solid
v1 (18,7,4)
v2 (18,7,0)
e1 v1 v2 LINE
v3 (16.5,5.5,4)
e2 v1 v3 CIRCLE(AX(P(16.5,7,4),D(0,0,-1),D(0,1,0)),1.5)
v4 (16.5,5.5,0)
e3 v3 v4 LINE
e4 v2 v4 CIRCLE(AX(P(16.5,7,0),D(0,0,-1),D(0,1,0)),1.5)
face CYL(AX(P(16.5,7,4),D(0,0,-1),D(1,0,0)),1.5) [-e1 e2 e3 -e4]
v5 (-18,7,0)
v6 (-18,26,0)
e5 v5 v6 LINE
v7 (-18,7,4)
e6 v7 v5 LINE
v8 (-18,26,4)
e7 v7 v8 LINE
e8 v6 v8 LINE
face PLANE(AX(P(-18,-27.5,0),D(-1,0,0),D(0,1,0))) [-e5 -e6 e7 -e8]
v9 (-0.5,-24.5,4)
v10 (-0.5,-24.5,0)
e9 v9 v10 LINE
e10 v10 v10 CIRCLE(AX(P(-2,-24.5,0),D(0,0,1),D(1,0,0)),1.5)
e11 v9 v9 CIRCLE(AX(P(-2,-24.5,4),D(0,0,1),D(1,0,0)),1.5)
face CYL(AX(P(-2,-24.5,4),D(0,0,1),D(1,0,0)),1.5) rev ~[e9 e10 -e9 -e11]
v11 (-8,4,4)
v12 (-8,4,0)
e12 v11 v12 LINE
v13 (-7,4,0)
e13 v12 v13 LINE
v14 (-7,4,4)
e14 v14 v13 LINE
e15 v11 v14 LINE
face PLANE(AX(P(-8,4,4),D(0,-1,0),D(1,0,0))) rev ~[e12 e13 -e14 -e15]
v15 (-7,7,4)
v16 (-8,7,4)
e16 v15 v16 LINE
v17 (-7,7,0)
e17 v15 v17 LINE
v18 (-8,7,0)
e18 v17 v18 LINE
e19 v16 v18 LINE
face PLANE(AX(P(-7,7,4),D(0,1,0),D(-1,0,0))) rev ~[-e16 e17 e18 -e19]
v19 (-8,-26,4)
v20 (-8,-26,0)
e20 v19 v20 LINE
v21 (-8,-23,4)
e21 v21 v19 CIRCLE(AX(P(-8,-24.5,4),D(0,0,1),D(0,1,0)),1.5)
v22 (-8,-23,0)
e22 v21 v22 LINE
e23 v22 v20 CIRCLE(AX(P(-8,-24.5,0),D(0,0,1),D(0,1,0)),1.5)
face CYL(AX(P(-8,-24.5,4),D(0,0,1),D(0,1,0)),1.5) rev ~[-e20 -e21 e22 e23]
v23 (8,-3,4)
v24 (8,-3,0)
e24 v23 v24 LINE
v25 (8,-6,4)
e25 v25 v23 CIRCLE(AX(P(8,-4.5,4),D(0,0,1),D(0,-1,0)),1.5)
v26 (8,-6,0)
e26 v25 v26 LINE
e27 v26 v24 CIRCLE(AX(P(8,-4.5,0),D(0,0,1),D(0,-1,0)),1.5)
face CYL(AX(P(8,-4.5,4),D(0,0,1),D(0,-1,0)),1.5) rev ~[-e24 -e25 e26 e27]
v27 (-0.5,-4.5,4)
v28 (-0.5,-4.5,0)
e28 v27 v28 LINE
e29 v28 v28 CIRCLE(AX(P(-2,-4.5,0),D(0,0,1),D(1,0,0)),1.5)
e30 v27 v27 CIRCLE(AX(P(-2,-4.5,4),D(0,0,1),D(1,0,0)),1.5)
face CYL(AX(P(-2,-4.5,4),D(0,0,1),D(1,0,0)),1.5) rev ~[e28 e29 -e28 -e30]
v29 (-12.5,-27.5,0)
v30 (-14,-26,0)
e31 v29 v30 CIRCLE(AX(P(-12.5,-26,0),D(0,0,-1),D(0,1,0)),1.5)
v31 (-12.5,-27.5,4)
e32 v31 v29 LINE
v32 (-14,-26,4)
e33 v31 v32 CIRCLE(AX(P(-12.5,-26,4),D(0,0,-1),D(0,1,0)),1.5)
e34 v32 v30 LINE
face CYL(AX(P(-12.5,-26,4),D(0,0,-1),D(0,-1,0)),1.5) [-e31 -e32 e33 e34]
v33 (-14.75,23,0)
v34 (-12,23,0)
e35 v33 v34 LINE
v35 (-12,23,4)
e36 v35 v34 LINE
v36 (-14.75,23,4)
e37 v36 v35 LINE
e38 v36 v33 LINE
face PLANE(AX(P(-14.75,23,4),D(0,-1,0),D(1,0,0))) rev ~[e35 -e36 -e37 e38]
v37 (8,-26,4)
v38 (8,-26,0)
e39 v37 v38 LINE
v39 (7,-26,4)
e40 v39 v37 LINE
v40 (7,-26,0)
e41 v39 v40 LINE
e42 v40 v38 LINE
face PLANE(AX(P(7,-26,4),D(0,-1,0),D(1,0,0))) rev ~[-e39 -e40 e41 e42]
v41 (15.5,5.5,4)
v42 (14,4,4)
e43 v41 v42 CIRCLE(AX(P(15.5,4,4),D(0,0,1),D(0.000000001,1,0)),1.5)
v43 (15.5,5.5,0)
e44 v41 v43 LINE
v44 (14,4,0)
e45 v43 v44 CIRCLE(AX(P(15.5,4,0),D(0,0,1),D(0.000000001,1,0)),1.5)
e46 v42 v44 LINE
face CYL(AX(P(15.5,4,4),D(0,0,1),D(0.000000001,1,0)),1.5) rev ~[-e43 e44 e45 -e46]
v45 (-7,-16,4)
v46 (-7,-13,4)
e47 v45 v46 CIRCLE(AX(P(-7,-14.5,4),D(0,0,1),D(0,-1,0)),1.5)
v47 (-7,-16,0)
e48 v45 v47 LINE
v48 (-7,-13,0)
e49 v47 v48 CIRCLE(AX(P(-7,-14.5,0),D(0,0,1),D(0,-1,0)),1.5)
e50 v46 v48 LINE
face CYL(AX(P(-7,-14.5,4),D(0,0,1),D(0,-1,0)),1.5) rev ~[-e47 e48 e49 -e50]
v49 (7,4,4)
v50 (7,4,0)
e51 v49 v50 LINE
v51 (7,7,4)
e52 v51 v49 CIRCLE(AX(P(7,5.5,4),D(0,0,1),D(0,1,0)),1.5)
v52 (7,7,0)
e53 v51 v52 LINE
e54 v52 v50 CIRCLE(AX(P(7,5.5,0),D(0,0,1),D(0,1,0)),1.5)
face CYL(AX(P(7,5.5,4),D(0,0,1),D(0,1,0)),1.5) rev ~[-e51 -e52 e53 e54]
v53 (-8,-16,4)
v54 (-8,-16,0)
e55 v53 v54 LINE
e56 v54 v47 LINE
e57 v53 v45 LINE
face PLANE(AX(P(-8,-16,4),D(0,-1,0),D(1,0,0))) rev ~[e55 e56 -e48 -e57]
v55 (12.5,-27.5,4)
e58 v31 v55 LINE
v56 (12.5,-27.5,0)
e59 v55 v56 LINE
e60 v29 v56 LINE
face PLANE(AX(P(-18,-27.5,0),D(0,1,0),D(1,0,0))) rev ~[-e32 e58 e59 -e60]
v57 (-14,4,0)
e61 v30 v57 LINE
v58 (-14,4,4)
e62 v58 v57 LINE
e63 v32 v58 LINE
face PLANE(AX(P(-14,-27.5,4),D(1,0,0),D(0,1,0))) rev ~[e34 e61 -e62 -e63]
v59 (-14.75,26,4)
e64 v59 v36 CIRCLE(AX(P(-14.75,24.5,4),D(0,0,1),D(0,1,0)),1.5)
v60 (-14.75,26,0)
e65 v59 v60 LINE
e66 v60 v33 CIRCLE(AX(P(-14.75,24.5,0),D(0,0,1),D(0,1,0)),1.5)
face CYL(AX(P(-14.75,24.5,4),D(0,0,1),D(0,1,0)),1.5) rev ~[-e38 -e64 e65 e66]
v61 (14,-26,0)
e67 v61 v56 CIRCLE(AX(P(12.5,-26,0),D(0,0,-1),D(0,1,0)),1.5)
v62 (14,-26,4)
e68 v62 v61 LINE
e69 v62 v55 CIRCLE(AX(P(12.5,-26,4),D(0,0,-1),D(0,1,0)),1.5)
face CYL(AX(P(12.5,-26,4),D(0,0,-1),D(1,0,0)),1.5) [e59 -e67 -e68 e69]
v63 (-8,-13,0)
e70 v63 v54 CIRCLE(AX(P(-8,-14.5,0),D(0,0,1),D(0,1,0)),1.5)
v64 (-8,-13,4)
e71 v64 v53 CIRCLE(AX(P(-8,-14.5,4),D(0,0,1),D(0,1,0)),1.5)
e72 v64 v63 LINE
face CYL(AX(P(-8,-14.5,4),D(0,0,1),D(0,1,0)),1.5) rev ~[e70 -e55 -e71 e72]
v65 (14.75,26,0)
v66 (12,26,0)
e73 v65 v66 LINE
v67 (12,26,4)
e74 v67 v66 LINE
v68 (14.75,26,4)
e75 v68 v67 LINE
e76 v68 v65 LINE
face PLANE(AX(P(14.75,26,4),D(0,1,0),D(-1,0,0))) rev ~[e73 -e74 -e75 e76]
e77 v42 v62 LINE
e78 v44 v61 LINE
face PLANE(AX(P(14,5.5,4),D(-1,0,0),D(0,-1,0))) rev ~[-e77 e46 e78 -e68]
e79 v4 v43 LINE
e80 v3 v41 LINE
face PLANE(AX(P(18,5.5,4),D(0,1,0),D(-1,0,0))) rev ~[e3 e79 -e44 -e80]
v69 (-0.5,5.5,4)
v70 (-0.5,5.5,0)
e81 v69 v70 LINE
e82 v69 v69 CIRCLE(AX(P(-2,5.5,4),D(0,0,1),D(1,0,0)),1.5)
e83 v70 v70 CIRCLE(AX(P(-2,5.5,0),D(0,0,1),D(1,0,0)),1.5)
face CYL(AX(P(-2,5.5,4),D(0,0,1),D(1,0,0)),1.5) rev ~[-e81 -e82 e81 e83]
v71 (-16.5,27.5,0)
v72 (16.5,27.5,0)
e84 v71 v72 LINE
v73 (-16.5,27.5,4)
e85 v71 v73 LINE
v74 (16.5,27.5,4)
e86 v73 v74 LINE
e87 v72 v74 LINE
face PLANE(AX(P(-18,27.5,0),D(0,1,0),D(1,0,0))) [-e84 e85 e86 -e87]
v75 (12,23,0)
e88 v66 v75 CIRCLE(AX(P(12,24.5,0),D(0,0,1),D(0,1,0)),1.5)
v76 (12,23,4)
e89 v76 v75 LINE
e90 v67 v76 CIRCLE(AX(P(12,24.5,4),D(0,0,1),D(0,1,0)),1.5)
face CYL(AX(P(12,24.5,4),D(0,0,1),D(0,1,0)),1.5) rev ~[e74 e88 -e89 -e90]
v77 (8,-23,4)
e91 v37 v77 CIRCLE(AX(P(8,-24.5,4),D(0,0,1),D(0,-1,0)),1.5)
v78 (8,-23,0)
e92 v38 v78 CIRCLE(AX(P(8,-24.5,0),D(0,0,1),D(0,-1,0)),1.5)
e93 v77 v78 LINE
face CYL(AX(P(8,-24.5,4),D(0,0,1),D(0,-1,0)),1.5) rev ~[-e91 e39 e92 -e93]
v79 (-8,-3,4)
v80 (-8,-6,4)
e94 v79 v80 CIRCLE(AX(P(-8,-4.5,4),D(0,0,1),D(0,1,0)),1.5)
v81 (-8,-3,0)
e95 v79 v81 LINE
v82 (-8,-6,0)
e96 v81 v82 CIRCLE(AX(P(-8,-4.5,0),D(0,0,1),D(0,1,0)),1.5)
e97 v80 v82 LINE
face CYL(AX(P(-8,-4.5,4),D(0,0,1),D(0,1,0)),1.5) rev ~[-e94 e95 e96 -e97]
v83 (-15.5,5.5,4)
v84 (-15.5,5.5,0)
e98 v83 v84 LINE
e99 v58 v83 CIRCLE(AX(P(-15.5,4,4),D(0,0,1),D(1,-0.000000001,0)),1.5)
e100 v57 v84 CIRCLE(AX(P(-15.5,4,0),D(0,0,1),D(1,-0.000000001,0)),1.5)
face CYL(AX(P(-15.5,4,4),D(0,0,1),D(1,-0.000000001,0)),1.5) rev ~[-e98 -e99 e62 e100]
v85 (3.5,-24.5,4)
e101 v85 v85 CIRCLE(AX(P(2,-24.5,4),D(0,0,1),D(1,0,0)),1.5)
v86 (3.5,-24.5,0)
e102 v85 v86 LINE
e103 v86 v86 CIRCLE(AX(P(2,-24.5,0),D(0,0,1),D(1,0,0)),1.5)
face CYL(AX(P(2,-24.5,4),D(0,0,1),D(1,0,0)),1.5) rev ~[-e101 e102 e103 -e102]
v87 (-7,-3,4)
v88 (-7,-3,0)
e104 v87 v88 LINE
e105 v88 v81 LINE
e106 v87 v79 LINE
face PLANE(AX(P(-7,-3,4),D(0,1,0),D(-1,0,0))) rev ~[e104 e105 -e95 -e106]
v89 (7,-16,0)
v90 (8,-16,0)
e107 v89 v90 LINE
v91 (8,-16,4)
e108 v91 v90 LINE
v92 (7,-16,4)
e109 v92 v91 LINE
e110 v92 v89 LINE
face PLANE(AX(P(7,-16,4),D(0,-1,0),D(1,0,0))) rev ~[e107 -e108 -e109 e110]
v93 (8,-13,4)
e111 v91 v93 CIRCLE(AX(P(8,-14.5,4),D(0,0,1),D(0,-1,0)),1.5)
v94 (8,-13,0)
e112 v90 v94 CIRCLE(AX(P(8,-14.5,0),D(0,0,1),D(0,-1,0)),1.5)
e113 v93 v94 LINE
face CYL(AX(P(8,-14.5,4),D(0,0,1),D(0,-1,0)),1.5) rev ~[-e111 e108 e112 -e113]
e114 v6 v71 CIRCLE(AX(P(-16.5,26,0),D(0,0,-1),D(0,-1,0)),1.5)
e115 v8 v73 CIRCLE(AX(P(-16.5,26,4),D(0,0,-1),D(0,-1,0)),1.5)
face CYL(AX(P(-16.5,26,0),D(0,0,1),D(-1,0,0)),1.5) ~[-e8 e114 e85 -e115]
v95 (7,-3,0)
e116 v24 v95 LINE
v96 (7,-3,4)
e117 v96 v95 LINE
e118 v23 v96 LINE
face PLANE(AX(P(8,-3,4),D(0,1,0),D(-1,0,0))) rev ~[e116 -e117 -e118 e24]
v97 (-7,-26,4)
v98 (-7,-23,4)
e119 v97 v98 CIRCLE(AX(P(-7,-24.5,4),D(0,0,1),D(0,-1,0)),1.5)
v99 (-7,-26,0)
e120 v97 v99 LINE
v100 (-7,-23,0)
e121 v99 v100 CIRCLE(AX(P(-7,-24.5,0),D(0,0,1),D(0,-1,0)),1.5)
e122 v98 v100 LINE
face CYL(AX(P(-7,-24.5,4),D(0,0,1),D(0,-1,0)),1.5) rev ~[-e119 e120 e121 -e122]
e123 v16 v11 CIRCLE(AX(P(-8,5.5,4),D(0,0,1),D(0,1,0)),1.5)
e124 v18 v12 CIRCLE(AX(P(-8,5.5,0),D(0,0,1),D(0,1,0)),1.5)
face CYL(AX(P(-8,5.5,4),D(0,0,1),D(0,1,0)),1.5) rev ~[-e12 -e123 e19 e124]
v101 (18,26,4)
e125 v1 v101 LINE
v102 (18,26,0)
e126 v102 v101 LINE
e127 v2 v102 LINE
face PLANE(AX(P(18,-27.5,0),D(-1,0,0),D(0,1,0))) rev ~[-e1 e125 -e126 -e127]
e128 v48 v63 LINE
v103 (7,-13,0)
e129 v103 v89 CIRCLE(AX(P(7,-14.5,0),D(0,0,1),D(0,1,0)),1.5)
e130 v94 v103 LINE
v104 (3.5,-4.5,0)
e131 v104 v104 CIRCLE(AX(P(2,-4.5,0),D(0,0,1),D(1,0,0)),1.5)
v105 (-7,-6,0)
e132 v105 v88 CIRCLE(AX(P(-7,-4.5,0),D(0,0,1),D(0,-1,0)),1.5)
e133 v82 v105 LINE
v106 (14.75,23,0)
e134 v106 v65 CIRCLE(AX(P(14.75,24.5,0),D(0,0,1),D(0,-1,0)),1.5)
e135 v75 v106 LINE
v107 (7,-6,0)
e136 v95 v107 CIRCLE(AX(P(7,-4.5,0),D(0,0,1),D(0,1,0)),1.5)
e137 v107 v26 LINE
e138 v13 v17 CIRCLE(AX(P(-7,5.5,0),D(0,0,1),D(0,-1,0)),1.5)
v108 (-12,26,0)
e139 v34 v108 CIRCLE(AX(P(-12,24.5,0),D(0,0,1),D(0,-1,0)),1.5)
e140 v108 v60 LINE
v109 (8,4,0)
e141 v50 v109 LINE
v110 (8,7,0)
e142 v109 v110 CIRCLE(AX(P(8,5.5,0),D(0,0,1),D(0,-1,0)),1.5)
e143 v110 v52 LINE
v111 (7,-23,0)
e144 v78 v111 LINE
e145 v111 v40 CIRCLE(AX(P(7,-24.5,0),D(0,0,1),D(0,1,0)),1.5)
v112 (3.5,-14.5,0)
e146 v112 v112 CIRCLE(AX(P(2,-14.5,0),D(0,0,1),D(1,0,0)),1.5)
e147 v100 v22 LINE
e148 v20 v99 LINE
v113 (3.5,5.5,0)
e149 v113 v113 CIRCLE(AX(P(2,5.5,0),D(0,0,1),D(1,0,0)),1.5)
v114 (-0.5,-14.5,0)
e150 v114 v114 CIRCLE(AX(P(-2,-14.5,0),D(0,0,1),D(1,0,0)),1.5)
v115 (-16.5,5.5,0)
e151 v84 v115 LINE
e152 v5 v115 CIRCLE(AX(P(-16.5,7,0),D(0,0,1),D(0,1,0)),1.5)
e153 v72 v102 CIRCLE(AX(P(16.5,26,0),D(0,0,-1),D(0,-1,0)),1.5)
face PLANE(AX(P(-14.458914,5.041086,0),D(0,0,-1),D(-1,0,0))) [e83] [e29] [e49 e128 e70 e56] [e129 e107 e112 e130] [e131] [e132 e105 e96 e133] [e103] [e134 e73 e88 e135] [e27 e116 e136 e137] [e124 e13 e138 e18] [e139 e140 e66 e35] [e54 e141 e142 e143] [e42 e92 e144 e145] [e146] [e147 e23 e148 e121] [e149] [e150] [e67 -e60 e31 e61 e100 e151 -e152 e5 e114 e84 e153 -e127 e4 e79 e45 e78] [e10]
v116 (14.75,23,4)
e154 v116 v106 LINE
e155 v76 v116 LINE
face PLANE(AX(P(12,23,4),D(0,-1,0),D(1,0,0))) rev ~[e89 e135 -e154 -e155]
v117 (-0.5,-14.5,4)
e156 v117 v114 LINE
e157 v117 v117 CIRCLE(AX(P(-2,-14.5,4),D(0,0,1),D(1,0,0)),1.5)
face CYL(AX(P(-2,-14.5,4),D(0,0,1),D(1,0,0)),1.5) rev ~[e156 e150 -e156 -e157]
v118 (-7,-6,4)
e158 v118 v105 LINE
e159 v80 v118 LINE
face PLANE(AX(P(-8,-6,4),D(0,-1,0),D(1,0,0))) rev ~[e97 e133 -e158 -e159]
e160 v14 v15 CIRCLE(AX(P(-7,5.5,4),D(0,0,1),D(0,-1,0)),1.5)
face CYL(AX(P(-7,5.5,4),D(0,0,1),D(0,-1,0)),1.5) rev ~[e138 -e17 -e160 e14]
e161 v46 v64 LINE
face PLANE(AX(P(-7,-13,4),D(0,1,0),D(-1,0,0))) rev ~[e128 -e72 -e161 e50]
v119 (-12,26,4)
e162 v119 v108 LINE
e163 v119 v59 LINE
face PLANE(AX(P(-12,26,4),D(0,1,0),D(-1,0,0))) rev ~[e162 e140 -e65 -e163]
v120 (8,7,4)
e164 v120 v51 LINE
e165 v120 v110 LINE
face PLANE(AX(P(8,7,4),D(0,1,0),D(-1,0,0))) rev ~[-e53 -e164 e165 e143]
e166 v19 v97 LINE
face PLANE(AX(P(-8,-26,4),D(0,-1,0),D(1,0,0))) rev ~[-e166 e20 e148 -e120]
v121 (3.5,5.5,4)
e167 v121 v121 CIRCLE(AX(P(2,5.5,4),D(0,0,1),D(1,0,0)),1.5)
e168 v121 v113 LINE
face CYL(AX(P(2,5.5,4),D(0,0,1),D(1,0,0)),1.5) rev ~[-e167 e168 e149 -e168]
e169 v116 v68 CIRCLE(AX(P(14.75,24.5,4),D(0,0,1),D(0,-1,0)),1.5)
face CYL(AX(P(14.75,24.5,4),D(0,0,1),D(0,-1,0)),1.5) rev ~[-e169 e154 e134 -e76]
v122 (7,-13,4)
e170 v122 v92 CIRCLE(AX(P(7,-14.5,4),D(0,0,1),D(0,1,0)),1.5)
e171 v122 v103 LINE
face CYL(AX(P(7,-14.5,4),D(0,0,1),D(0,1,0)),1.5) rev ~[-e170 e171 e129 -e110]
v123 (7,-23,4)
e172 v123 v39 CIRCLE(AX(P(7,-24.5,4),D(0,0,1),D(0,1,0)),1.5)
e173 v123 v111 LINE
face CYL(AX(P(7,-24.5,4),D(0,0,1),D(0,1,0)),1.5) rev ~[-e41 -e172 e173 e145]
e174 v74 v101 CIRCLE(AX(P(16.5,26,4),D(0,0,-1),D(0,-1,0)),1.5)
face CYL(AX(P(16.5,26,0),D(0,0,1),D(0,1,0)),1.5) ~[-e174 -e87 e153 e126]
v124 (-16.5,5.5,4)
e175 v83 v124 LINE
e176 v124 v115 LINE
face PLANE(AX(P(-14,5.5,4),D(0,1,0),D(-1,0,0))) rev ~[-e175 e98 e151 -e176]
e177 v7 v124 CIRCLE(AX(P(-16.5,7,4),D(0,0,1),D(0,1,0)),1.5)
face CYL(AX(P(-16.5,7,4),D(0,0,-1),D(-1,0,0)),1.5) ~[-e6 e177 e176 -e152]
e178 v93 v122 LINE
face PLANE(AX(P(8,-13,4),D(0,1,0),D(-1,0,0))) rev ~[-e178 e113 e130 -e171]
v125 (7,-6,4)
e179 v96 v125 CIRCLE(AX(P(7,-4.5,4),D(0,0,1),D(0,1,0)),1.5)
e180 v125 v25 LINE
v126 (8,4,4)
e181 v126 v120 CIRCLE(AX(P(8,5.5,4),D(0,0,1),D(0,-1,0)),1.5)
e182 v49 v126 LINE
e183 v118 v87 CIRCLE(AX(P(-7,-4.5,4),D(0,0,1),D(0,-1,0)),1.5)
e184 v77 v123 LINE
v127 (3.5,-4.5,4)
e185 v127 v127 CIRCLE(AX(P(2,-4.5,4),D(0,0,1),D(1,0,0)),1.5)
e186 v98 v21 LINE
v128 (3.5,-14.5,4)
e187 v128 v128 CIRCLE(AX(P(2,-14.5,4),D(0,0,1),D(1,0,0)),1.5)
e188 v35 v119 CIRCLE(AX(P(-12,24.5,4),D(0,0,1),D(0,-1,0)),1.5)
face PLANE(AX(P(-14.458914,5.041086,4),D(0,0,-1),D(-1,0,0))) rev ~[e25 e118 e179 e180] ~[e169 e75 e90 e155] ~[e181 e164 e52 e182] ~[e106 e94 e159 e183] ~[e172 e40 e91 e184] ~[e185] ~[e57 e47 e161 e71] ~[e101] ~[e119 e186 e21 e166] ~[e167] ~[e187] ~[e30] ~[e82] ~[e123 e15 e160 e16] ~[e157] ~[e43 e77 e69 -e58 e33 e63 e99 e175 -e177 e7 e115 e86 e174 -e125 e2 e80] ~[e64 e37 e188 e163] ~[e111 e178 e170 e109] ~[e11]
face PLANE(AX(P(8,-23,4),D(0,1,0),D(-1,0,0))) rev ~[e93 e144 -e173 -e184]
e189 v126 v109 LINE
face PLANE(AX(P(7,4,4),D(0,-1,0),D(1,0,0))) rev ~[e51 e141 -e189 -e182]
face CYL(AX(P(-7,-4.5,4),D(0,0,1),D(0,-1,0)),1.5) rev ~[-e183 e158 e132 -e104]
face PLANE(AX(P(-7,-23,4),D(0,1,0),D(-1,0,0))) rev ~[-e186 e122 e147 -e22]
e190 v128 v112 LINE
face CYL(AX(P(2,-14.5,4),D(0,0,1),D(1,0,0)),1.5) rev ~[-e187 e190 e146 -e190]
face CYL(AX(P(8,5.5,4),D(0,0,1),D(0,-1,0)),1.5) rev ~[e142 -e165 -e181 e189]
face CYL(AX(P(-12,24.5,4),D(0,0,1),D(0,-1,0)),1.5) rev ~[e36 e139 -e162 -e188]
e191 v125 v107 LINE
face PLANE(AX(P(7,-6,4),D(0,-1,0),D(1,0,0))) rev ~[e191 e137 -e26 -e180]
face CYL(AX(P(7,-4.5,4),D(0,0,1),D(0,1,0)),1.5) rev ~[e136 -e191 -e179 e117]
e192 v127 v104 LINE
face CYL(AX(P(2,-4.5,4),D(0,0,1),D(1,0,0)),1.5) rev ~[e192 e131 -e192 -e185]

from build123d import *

# Parameters (mm, degrees)
SKETCH1_W           = 36
SKETCH1_H           = 55
BOSS_EXTRUDE1_DEPTH = 4
SKETCH2_R           = 1.5
CUT_EXTRUDE1_DEPTH  = 4
FILLET1_R           = 1.5
BOSS_EXTRUDE2_DEPTH = 4


with BuildPart() as part:
    # Sketch1 → Boss-Extrude1 (new body)
    with BuildSketch(Plane.XY):
        Rectangle(SKETCH1_W, SKETCH1_H)
    extrude(amount=BOSS_EXTRUDE1_DEPTH)

    # Sketch2 → Cut-Extrude1 (cut)
    with BuildSketch(Plane.XY.offset(4)):
        with BuildLine():
            Line((-14.75, 23), (-12, 23))
            ThreePointArc((-12, 23), (-10.5, 24.5), (-12, 26))
            Line((-12, 26), (-14.75, 26))
            ThreePointArc((-14.75, 26), (-16.25, 24.5), (-14.75, 23))
        make_face()
        with BuildLine():
            Line((12, 23), (14.75, 23))
            ThreePointArc((14.75, 23), (16.25, 24.5), (14.75, 26))
            Line((14.75, 26), (12, 26))
            ThreePointArc((12, 26), (10.5, 24.5), (12, 23))
        make_face()
        with BuildLine():
            Line((-8, 4), (-7, 4))
            ThreePointArc((-7, 4), (-5.5, 5.5), (-7, 7))
            Line((-7, 7), (-8, 7))
            ThreePointArc((-8, 7), (-9.5, 5.5), (-8, 4))
        make_face()
        with Locations((-2, 5.5)):
            Circle(SKETCH2_R)
        with Locations((2, 5.5)):
            Circle(SKETCH2_R)
        with BuildLine():
            Line((7, 4), (8, 4))
            ThreePointArc((8, 4), (9.5, 5.5), (8, 7))
            Line((8, 7), (7, 7))
            ThreePointArc((7, 7), (5.5, 5.5), (7, 4))
        make_face()
        with BuildLine():
            Line((7, -6), (8, -6))
            ThreePointArc((8, -6), (9.5, -4.5), (8, -3))
            Line((8, -3), (7, -3))
            ThreePointArc((7, -3), (5.5, -4.5), (7, -6))
        make_face()
        with Locations((2, -4.5)):
            Circle(SKETCH2_R)
        with Locations((-2, -4.5)):
            Circle(SKETCH2_R)
        with BuildLine():
            Line((-8, -6), (-7, -6))
            ThreePointArc((-7, -6), (-5.5, -4.5), (-7, -3))
            Line((-7, -3), (-8, -3))
            ThreePointArc((-8, -3), (-9.5, -4.5), (-8, -6))
        make_face()
        with BuildLine():
            Line((-8, -16), (-7, -16))
            ThreePointArc((-7, -16), (-5.5, -14.5), (-7, -13))
            Line((-7, -13), (-8, -13))
            ThreePointArc((-8, -13), (-9.5, -14.5), (-8, -16))
        make_face()
        with BuildLine():
            Line((-8, -26), (-7, -26))
            ThreePointArc((-7, -26), (-5.5, -24.5), (-7, -23))
            Line((-7, -23), (-8, -23))
            ThreePointArc((-8, -23), (-9.5, -24.5), (-8, -26))
        make_face()
        with Locations((-2, -14.5)):
            Circle(SKETCH2_R)
        with Locations((-2, -24.5)):
            Circle(SKETCH2_R)
        with Locations((2, -14.5)):
            Circle(SKETCH2_R)
        with Locations((2, -24.5)):
            Circle(SKETCH2_R)
        with BuildLine():
            Line((7, -26), (8, -26))
            ThreePointArc((8, -26), (9.5, -24.5), (8, -23))
            Line((8, -23), (7, -23))
            ThreePointArc((7, -23), (5.5, -24.5), (7, -26))
        make_face()
        Polygon((-14, 5.5), (-18, 5.5), (-18, -26), (-18, -27.5), (-16.5, -27.5), (-14, -27.5), align=None)
        Polygon((14, 5.5), (14, -27.5), (16.5, -27.5), (18, -27.5), (18, -26), (18, 5.5), align=None)
        with BuildLine():
            ThreePointArc((7, -13), (5.5, -14.5), (7, -16))
            Line((7, -16), (8, -16))
            ThreePointArc((8, -16), (9.5, -14.5), (8, -13))
            Line((8, -13), (7, -13))
        make_face()
    extrude(amount=-CUT_EXTRUDE1_DEPTH, mode=Mode.SUBTRACT)

    # Fillet1
    fillet1_edges = [part.edges().sort_by_distance(p)[0] for p in [
        (18, 5.5, 2),
        (14, -27.5, 2),
        (-14, -27.5, 2),
        (-18, 5.5, 2),
        (-18, 27.5, 2),
        (18, 27.5, 2),
    ]]
    fillet(fillet1_edges, radius=FILLET1_R)

    # Sketch3 → Boss-Extrude2 (add)
    with BuildSketch(Plane.XY.offset(4)):
        with BuildLine():
            Line((-14, 5.5), (-14, 4))
            ThreePointArc((-14, 4), (-14.439339828, 5.060660172), (-15.5, 5.5))
            Line((-15.5, 5.5), (-14, 5.5))
        make_face()
        with BuildLine():
            ThreePointArc((15.5, 5.5), (14.439339828, 5.060660172), (14, 4))
            Line((14, 4), (14, 5.5))
            Line((14, 5.5), (15.5, 5.5))
        make_face()
    extrude(amount=-BOSS_EXTRUDE2_DEPTH)


solid = part.part
